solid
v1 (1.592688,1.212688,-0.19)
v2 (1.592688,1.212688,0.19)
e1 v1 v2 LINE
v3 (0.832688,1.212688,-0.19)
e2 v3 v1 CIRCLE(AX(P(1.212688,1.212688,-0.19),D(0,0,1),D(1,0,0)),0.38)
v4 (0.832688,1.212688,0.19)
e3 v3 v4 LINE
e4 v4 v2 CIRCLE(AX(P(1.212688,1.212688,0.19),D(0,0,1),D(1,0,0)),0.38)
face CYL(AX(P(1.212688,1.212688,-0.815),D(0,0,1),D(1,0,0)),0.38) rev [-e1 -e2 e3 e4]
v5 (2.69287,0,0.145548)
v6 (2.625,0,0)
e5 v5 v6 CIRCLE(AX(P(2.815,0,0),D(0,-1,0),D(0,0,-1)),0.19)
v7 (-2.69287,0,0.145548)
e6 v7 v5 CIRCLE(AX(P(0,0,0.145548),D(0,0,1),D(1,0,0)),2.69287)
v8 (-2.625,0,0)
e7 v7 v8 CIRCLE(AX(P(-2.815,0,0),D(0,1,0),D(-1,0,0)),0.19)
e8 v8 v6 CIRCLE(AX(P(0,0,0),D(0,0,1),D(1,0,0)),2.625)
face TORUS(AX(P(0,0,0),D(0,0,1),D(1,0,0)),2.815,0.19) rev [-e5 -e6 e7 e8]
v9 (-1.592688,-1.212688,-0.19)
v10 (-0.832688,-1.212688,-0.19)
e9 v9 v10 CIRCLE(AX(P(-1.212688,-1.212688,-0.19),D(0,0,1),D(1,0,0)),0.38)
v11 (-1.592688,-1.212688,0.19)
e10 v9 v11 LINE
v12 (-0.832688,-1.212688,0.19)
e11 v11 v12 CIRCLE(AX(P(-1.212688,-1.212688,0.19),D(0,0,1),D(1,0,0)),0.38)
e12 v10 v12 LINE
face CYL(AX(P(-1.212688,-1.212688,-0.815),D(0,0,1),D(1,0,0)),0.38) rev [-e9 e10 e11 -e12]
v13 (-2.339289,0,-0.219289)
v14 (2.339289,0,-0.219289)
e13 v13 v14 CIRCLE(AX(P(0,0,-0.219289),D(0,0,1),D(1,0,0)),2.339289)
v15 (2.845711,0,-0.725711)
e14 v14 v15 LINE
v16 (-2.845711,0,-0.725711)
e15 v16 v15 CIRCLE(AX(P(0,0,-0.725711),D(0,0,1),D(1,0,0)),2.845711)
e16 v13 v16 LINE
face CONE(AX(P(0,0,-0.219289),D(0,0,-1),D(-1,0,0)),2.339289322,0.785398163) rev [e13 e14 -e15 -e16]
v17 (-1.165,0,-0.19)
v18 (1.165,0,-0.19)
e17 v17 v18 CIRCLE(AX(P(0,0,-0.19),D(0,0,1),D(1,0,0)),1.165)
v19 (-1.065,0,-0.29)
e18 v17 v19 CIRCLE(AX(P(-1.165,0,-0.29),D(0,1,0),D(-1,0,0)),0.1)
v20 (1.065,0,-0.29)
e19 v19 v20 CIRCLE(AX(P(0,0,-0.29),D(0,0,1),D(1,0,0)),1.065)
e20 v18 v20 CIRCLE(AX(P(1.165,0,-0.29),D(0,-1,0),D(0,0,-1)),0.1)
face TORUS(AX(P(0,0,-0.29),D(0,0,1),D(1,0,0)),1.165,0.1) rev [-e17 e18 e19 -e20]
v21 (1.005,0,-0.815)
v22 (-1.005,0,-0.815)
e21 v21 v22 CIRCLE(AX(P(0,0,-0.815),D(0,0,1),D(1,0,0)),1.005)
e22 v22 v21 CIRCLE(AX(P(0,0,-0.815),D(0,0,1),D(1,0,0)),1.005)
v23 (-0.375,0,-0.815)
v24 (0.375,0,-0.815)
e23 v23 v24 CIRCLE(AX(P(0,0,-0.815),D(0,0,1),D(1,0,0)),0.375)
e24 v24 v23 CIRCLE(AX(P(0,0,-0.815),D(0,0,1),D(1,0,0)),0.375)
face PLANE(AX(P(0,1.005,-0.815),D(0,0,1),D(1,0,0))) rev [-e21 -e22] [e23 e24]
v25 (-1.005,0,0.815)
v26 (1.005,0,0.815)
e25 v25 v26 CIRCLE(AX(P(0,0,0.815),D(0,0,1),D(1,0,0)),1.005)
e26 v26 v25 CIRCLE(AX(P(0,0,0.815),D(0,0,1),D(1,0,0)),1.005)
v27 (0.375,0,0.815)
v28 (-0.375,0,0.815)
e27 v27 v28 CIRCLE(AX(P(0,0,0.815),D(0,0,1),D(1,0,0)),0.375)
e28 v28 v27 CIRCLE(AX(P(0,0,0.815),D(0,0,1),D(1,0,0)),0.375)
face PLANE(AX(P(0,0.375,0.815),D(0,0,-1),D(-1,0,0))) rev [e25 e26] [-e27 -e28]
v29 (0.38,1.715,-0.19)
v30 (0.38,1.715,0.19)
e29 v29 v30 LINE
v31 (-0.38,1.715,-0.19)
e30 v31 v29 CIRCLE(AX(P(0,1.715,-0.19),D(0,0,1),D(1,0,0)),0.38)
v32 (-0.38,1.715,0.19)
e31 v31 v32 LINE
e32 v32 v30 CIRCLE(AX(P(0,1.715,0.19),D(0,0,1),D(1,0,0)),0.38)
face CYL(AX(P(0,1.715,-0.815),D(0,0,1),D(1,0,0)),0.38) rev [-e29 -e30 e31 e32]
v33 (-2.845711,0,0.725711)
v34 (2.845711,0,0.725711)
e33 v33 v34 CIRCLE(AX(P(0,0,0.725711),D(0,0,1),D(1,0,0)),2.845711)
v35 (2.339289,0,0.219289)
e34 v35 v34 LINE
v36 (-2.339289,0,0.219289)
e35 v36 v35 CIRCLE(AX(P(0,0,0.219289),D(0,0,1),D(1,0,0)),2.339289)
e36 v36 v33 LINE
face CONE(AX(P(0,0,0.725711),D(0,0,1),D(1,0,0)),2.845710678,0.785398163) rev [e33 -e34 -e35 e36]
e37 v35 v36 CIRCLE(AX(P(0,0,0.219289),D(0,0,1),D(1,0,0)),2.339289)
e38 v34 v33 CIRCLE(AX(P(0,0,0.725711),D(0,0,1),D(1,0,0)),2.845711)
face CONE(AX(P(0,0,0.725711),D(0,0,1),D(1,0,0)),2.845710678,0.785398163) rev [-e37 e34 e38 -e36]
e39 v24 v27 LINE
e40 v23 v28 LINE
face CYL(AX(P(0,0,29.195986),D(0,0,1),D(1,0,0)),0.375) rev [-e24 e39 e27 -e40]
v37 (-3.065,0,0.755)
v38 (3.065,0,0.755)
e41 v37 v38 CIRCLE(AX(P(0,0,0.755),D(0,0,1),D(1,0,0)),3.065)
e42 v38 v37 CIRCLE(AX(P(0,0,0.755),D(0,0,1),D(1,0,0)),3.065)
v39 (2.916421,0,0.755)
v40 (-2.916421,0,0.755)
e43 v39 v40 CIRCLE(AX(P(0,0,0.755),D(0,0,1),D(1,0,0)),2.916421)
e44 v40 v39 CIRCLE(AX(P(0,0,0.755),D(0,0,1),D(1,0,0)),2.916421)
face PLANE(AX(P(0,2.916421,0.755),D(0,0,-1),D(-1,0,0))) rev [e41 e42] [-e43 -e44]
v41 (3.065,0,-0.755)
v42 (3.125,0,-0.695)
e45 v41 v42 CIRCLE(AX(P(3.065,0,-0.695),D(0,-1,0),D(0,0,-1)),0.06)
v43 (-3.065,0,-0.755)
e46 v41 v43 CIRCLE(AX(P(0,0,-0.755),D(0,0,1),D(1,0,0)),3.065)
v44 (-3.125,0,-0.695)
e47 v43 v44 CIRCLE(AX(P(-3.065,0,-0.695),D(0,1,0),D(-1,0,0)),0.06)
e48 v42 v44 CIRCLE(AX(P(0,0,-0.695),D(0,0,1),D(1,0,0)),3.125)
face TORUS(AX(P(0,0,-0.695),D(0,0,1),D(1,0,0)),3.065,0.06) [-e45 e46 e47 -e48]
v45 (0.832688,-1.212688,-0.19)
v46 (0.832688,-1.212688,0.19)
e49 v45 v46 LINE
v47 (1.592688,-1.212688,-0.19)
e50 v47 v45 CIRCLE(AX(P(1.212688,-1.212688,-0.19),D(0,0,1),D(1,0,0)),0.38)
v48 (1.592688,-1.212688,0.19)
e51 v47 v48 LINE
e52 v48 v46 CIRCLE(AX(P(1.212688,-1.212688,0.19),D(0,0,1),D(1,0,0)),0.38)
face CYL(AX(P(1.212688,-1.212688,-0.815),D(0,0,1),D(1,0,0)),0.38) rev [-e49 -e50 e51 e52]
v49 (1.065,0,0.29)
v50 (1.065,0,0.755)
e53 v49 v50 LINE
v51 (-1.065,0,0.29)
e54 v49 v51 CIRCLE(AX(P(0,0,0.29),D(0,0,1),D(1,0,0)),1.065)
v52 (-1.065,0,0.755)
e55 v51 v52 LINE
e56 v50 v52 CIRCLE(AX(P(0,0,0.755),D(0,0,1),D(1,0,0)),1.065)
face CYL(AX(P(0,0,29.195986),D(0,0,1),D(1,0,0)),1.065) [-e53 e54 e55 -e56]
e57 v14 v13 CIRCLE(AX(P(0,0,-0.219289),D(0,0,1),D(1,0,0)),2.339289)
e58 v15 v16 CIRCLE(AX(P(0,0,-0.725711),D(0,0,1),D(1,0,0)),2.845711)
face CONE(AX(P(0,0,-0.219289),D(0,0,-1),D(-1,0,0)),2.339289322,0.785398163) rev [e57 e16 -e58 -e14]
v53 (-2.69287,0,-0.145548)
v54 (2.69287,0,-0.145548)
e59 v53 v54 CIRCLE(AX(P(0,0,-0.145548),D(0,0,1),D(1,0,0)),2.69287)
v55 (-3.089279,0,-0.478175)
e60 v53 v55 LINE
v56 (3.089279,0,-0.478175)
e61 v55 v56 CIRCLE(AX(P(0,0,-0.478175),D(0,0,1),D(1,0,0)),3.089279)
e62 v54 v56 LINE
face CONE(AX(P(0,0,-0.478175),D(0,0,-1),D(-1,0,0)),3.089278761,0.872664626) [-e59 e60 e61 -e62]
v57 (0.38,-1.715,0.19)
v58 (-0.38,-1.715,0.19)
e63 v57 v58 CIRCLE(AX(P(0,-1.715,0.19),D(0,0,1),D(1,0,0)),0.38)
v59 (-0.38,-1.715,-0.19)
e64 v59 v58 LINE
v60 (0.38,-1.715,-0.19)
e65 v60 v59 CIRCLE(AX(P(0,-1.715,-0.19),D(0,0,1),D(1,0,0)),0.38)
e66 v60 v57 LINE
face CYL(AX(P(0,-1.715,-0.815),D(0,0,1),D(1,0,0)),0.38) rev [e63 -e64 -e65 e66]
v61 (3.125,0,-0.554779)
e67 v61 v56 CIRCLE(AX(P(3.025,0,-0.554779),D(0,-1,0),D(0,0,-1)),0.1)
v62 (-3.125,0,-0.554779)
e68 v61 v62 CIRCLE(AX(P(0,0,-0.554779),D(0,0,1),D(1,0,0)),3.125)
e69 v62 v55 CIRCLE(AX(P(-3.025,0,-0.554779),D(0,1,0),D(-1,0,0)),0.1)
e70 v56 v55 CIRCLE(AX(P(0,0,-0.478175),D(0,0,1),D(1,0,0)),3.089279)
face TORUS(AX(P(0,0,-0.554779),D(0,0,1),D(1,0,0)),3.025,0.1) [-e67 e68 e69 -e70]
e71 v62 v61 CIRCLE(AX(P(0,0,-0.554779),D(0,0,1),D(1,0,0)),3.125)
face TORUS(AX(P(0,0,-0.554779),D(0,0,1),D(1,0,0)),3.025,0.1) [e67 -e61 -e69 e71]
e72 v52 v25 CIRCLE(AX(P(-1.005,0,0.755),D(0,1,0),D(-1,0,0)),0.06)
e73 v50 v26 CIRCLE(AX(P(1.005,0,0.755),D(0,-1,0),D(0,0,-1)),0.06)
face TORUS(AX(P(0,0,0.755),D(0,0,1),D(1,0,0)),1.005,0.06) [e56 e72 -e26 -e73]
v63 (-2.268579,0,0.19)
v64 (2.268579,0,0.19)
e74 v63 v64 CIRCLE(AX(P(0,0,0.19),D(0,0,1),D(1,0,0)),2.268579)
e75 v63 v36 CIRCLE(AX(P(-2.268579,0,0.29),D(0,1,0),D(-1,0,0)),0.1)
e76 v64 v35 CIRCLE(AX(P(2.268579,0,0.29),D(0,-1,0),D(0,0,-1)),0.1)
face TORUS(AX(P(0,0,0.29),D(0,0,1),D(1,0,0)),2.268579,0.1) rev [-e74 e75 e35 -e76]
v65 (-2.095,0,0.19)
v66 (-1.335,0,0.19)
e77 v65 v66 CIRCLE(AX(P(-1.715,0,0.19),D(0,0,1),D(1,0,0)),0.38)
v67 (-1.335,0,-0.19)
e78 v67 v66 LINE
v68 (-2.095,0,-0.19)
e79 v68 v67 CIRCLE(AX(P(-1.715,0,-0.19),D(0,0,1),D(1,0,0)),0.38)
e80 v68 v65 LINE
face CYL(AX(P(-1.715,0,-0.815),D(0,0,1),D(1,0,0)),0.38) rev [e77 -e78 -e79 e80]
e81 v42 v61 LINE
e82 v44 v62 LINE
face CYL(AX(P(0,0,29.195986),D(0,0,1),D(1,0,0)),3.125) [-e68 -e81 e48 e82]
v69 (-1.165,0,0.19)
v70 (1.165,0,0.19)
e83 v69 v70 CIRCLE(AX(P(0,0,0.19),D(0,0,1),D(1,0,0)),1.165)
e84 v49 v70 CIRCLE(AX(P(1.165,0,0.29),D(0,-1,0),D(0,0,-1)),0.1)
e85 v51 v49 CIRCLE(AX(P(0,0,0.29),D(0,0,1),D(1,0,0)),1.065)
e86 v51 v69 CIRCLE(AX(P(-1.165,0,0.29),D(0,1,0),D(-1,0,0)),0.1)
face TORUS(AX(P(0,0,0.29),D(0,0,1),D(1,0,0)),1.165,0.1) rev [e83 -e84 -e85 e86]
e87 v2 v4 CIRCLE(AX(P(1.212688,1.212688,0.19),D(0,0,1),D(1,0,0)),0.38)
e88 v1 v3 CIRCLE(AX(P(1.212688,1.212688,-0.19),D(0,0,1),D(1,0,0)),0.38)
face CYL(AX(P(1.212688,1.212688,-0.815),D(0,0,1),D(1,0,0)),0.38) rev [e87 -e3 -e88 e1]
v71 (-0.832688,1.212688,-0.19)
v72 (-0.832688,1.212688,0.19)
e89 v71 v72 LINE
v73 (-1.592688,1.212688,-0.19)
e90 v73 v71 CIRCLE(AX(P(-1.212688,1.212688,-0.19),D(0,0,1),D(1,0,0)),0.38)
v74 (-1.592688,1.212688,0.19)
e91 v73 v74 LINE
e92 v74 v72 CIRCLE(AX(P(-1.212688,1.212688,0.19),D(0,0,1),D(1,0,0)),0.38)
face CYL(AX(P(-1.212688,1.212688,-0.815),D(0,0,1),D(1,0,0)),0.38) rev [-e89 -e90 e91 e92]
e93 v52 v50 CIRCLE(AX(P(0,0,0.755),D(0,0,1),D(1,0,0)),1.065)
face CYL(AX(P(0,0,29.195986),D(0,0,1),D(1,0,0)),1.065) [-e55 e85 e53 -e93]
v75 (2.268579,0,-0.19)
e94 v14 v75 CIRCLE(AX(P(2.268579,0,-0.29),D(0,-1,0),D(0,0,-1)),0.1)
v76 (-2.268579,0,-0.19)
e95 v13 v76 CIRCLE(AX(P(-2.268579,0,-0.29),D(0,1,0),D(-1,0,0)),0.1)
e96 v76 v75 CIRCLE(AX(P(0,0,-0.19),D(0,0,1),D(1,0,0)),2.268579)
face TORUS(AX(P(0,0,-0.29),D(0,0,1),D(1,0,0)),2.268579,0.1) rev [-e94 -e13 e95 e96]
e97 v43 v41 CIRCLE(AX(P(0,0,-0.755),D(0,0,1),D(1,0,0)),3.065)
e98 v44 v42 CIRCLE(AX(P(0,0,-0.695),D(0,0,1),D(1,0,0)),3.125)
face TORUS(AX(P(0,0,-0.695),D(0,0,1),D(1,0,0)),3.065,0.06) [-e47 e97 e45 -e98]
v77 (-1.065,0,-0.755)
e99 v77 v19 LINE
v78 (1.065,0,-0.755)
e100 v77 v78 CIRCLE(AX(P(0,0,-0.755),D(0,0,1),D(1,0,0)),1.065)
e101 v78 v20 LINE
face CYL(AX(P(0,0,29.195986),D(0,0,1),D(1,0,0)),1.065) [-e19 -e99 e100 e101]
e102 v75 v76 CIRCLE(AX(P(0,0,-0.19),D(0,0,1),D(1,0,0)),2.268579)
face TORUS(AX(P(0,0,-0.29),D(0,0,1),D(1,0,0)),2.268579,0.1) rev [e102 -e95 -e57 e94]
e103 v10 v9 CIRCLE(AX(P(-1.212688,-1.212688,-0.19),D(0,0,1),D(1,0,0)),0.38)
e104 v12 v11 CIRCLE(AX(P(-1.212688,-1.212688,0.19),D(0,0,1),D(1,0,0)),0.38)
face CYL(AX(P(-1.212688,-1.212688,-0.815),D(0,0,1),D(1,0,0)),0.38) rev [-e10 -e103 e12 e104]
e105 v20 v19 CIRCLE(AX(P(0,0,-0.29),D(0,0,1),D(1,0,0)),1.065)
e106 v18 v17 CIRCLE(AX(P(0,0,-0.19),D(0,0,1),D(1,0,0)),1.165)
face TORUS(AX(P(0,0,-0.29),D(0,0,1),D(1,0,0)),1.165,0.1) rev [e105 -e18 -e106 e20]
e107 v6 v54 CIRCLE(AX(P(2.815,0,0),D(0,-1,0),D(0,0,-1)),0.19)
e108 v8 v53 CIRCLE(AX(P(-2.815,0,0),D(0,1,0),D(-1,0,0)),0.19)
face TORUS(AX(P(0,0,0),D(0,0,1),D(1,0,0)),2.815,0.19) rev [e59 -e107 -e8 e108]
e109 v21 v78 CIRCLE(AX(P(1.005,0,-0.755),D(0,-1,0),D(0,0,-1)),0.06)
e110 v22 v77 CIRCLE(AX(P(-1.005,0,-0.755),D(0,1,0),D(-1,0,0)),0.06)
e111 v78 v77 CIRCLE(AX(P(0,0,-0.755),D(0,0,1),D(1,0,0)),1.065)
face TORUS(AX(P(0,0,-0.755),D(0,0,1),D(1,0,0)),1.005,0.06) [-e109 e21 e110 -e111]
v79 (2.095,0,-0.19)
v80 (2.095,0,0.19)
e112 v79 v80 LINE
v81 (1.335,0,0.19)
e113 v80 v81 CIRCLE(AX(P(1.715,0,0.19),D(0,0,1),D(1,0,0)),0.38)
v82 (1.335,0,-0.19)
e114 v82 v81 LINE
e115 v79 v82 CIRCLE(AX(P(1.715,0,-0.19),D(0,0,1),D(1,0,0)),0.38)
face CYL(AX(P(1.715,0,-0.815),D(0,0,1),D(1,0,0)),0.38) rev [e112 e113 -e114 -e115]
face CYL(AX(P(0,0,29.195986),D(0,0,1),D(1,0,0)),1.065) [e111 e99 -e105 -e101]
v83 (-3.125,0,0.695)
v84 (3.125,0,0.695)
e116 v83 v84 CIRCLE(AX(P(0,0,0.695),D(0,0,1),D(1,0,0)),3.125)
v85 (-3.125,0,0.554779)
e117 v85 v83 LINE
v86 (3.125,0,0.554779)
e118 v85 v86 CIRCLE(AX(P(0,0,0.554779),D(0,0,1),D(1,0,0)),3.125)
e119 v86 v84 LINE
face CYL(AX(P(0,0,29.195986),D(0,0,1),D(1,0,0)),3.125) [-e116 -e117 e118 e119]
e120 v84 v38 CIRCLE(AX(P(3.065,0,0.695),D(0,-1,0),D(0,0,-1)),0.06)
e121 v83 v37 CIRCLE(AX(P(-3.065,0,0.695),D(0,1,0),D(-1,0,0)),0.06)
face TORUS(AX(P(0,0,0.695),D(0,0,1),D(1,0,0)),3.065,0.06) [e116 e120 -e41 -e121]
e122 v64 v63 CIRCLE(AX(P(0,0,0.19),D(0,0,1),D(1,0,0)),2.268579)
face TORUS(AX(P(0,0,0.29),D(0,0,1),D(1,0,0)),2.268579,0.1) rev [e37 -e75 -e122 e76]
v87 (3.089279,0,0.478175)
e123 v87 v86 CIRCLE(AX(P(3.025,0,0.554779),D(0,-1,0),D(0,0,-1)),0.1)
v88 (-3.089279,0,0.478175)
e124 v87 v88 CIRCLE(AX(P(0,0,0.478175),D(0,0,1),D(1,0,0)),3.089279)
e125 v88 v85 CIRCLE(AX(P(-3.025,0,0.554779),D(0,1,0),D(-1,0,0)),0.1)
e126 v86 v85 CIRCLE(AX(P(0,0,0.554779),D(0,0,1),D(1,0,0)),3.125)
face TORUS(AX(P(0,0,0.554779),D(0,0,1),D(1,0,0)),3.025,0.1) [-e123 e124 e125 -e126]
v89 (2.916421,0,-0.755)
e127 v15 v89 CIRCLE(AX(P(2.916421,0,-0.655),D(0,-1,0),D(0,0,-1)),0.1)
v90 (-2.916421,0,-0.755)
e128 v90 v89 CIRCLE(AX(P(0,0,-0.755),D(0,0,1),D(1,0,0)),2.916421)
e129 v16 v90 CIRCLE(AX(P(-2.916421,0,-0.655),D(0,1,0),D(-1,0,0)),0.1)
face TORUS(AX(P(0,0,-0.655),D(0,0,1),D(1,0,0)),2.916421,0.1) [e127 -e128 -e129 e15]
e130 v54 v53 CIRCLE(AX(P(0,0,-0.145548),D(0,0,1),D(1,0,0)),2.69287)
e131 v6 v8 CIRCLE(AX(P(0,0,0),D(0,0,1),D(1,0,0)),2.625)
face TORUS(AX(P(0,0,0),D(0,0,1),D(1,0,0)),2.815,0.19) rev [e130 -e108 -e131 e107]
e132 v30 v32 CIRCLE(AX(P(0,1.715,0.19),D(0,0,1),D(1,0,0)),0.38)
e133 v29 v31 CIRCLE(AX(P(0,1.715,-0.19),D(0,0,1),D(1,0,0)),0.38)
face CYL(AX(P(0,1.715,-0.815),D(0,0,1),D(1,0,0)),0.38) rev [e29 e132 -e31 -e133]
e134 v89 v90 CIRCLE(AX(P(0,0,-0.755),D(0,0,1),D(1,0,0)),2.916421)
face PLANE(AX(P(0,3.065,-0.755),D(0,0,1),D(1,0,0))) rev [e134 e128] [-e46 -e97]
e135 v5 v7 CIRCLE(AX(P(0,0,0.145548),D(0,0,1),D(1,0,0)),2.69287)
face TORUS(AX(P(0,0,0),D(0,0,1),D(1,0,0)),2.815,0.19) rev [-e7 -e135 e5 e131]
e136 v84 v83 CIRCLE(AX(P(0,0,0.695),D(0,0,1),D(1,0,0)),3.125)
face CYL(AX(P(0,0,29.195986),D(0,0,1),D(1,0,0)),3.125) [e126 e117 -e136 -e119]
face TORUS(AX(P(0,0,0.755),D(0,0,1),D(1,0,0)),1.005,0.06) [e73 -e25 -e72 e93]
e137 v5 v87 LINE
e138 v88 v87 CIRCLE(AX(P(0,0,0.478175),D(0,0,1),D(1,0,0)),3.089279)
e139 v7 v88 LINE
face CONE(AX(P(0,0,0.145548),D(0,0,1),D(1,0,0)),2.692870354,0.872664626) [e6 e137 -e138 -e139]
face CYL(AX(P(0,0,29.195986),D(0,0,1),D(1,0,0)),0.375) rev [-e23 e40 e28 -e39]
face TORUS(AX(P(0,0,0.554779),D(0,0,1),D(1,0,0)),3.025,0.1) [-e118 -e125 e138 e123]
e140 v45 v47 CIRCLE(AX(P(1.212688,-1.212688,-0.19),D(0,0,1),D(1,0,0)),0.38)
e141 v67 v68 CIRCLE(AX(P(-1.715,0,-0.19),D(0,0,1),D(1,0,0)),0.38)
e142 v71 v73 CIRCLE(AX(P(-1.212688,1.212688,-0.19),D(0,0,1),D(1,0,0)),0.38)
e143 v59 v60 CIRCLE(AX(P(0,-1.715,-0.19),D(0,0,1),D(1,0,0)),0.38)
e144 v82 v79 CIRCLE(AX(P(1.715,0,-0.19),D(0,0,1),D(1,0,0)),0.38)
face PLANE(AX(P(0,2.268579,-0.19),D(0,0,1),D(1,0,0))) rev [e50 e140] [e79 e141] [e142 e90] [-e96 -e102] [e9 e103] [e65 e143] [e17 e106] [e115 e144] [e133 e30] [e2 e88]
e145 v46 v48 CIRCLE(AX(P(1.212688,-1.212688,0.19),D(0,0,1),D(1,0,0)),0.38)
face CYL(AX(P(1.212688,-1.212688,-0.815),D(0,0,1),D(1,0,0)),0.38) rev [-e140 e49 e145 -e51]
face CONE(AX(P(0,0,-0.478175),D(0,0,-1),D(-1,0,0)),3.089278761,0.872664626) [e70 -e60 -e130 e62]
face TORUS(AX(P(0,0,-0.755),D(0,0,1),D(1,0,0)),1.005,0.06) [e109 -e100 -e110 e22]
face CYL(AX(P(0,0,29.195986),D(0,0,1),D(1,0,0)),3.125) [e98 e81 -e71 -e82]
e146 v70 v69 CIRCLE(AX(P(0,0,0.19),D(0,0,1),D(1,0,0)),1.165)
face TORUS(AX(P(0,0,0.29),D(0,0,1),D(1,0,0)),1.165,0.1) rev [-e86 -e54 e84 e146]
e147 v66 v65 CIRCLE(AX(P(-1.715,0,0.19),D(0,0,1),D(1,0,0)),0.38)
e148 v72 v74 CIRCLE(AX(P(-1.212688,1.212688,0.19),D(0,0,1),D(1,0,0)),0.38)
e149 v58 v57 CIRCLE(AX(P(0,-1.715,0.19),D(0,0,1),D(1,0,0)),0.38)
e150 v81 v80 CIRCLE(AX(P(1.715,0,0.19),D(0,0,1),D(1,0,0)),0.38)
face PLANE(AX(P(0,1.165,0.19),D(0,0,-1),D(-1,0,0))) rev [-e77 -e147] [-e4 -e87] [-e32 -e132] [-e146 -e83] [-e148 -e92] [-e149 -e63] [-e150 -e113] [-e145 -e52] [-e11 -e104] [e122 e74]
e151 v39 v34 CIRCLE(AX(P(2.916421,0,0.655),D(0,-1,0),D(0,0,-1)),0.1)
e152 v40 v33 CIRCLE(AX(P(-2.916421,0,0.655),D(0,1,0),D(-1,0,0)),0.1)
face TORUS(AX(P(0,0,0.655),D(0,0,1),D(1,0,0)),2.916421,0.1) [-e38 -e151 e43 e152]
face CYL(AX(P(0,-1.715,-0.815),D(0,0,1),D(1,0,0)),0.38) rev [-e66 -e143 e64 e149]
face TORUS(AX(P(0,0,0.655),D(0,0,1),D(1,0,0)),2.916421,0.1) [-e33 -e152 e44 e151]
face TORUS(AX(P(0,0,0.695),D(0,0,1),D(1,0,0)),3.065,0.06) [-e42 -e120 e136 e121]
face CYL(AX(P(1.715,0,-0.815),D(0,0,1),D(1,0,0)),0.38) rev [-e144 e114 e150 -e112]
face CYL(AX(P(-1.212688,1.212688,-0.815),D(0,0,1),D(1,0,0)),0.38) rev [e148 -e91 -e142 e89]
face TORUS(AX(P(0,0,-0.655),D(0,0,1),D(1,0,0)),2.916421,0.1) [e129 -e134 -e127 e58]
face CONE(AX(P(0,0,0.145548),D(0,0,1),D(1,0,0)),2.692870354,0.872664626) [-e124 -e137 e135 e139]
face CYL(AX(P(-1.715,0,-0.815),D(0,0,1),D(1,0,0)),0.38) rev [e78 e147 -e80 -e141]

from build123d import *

# Parameters (mm, degrees)
LIGHTENING_HOLES_SKETCH_R      = 0.38
LIGHTENING_HOLES_8X_0_76_DEPTH = 5.532248476


with BuildPart() as part:
    # Pulley Profile Sketch → Pulley Body (revolve)
    with BuildSketch(Plane(origin=(0, 0, 0), x_dir=(0, 0, -1), z_dir=(1, 0, 0)), mode=Mode.PRIVATE) as pulley_body_sk:
        with BuildLine():
            Line((0.815, 0.375), (-0.815, 0.375))
            Line((-0.815, 0.375), (-0.815, 1.005))
            ThreePointArc((-0.815, 1.005), (-0.797426407, 1.047426407), (-0.755, 1.065))
            Line((-0.755, 1.065), (-0.29, 1.065))
            ThreePointArc((-0.29, 1.065), (-0.219289322, 1.094289322), (-0.19, 1.165))
            Line((-0.19, 1.165), (-0.19, 2.268578644))
            ThreePointArc((-0.19, 2.268578644), (-0.197612047, 2.306846987), (-0.219289322, 2.339289322))
            Line((-0.219289322, 2.339289322), (-0.725710678, 2.845710678))
            ThreePointArc((-0.725710678, 2.845710678), (-0.747387953, 2.878153013), (-0.755, 2.916421356))
            Line((-0.755, 2.916421356), (-0.755, 3.065))
            ThreePointArc((-0.755, 3.065), (-0.737426407, 3.107426407), (-0.695, 3.125))
            Line((-0.695, 3.125), (-0.554779036, 3.125))
            ThreePointArc((-0.554779036, 3.125), (-0.51251721, 3.115630779), (-0.478174592, 3.089278761))
            Line((-0.478174592, 3.089278761), (-0.145548444, 2.692870354))
            ThreePointArc((-0.145548444, 2.692870354), (0, 2.625), (0.145548444, 2.692870354))
            Line((0.145548444, 2.692870354), (0.478174592, 3.089278761))
            ThreePointArc((0.478174592, 3.089278761), (0.51251721, 3.115630779), (0.554779036, 3.125))
            Line((0.554779036, 3.125), (0.695, 3.125))
            ThreePointArc((0.695, 3.125), (0.737426407, 3.107426407), (0.755, 3.065))
            Line((0.755, 3.065), (0.755, 2.916421356))
            ThreePointArc((0.755, 2.916421356), (0.747387953, 2.878153013), (0.725710678, 2.845710678))
            Line((0.725710678, 2.845710678), (0.219289322, 2.339289322))
            ThreePointArc((0.219289322, 2.339289322), (0.197612047, 2.306846987), (0.19, 2.268578644))
            Line((0.19, 2.268578644), (0.19, 1.165))
            ThreePointArc((0.19, 1.165), (0.219289322, 1.094289322), (0.29, 1.065))
            Line((0.29, 1.065), (0.755, 1.065))
            ThreePointArc((0.755, 1.065), (0.797426407, 1.047426407), (0.815, 1.005))
            Line((0.815, 1.005), (0.815, 0.375))
        make_face()
    revolve(pulley_body_sk.sketch.rotate(Axis((0, 0, 29.195986036), (0, 0, -1)), 90), axis=Axis((0, 0, 29.195986036), (0, 0, -1)))

    # Lightening Holes Sketch → Lightening Holes 8xØ0.76 (cut, through all)
    with BuildSketch(Plane.XY.offset(0.19)):
        with Locations((0, 1.715)):
            Circle(LIGHTENING_HOLES_SKETCH_R)
        with Locations((-1.21268813, 1.21268813)):
            Circle(LIGHTENING_HOLES_SKETCH_R)
        with Locations((-1.715, 0)):
            Circle(LIGHTENING_HOLES_SKETCH_R)
        with Locations((-1.21268813, -1.21268813)):
            Circle(LIGHTENING_HOLES_SKETCH_R)
        with Locations((0, -1.715)):
            Circle(LIGHTENING_HOLES_SKETCH_R)
        with Locations((1.21268813, -1.21268813)):
            Circle(LIGHTENING_HOLES_SKETCH_R)
        with Locations((1.715, 0)):
            Circle(LIGHTENING_HOLES_SKETCH_R)
        with Locations((1.21268813, 1.21268813)):
            Circle(LIGHTENING_HOLES_SKETCH_R)
    extrude(amount=-LIGHTENING_HOLES_8X_0_76_DEPTH, mode=Mode.SUBTRACT)


solid = part.part
